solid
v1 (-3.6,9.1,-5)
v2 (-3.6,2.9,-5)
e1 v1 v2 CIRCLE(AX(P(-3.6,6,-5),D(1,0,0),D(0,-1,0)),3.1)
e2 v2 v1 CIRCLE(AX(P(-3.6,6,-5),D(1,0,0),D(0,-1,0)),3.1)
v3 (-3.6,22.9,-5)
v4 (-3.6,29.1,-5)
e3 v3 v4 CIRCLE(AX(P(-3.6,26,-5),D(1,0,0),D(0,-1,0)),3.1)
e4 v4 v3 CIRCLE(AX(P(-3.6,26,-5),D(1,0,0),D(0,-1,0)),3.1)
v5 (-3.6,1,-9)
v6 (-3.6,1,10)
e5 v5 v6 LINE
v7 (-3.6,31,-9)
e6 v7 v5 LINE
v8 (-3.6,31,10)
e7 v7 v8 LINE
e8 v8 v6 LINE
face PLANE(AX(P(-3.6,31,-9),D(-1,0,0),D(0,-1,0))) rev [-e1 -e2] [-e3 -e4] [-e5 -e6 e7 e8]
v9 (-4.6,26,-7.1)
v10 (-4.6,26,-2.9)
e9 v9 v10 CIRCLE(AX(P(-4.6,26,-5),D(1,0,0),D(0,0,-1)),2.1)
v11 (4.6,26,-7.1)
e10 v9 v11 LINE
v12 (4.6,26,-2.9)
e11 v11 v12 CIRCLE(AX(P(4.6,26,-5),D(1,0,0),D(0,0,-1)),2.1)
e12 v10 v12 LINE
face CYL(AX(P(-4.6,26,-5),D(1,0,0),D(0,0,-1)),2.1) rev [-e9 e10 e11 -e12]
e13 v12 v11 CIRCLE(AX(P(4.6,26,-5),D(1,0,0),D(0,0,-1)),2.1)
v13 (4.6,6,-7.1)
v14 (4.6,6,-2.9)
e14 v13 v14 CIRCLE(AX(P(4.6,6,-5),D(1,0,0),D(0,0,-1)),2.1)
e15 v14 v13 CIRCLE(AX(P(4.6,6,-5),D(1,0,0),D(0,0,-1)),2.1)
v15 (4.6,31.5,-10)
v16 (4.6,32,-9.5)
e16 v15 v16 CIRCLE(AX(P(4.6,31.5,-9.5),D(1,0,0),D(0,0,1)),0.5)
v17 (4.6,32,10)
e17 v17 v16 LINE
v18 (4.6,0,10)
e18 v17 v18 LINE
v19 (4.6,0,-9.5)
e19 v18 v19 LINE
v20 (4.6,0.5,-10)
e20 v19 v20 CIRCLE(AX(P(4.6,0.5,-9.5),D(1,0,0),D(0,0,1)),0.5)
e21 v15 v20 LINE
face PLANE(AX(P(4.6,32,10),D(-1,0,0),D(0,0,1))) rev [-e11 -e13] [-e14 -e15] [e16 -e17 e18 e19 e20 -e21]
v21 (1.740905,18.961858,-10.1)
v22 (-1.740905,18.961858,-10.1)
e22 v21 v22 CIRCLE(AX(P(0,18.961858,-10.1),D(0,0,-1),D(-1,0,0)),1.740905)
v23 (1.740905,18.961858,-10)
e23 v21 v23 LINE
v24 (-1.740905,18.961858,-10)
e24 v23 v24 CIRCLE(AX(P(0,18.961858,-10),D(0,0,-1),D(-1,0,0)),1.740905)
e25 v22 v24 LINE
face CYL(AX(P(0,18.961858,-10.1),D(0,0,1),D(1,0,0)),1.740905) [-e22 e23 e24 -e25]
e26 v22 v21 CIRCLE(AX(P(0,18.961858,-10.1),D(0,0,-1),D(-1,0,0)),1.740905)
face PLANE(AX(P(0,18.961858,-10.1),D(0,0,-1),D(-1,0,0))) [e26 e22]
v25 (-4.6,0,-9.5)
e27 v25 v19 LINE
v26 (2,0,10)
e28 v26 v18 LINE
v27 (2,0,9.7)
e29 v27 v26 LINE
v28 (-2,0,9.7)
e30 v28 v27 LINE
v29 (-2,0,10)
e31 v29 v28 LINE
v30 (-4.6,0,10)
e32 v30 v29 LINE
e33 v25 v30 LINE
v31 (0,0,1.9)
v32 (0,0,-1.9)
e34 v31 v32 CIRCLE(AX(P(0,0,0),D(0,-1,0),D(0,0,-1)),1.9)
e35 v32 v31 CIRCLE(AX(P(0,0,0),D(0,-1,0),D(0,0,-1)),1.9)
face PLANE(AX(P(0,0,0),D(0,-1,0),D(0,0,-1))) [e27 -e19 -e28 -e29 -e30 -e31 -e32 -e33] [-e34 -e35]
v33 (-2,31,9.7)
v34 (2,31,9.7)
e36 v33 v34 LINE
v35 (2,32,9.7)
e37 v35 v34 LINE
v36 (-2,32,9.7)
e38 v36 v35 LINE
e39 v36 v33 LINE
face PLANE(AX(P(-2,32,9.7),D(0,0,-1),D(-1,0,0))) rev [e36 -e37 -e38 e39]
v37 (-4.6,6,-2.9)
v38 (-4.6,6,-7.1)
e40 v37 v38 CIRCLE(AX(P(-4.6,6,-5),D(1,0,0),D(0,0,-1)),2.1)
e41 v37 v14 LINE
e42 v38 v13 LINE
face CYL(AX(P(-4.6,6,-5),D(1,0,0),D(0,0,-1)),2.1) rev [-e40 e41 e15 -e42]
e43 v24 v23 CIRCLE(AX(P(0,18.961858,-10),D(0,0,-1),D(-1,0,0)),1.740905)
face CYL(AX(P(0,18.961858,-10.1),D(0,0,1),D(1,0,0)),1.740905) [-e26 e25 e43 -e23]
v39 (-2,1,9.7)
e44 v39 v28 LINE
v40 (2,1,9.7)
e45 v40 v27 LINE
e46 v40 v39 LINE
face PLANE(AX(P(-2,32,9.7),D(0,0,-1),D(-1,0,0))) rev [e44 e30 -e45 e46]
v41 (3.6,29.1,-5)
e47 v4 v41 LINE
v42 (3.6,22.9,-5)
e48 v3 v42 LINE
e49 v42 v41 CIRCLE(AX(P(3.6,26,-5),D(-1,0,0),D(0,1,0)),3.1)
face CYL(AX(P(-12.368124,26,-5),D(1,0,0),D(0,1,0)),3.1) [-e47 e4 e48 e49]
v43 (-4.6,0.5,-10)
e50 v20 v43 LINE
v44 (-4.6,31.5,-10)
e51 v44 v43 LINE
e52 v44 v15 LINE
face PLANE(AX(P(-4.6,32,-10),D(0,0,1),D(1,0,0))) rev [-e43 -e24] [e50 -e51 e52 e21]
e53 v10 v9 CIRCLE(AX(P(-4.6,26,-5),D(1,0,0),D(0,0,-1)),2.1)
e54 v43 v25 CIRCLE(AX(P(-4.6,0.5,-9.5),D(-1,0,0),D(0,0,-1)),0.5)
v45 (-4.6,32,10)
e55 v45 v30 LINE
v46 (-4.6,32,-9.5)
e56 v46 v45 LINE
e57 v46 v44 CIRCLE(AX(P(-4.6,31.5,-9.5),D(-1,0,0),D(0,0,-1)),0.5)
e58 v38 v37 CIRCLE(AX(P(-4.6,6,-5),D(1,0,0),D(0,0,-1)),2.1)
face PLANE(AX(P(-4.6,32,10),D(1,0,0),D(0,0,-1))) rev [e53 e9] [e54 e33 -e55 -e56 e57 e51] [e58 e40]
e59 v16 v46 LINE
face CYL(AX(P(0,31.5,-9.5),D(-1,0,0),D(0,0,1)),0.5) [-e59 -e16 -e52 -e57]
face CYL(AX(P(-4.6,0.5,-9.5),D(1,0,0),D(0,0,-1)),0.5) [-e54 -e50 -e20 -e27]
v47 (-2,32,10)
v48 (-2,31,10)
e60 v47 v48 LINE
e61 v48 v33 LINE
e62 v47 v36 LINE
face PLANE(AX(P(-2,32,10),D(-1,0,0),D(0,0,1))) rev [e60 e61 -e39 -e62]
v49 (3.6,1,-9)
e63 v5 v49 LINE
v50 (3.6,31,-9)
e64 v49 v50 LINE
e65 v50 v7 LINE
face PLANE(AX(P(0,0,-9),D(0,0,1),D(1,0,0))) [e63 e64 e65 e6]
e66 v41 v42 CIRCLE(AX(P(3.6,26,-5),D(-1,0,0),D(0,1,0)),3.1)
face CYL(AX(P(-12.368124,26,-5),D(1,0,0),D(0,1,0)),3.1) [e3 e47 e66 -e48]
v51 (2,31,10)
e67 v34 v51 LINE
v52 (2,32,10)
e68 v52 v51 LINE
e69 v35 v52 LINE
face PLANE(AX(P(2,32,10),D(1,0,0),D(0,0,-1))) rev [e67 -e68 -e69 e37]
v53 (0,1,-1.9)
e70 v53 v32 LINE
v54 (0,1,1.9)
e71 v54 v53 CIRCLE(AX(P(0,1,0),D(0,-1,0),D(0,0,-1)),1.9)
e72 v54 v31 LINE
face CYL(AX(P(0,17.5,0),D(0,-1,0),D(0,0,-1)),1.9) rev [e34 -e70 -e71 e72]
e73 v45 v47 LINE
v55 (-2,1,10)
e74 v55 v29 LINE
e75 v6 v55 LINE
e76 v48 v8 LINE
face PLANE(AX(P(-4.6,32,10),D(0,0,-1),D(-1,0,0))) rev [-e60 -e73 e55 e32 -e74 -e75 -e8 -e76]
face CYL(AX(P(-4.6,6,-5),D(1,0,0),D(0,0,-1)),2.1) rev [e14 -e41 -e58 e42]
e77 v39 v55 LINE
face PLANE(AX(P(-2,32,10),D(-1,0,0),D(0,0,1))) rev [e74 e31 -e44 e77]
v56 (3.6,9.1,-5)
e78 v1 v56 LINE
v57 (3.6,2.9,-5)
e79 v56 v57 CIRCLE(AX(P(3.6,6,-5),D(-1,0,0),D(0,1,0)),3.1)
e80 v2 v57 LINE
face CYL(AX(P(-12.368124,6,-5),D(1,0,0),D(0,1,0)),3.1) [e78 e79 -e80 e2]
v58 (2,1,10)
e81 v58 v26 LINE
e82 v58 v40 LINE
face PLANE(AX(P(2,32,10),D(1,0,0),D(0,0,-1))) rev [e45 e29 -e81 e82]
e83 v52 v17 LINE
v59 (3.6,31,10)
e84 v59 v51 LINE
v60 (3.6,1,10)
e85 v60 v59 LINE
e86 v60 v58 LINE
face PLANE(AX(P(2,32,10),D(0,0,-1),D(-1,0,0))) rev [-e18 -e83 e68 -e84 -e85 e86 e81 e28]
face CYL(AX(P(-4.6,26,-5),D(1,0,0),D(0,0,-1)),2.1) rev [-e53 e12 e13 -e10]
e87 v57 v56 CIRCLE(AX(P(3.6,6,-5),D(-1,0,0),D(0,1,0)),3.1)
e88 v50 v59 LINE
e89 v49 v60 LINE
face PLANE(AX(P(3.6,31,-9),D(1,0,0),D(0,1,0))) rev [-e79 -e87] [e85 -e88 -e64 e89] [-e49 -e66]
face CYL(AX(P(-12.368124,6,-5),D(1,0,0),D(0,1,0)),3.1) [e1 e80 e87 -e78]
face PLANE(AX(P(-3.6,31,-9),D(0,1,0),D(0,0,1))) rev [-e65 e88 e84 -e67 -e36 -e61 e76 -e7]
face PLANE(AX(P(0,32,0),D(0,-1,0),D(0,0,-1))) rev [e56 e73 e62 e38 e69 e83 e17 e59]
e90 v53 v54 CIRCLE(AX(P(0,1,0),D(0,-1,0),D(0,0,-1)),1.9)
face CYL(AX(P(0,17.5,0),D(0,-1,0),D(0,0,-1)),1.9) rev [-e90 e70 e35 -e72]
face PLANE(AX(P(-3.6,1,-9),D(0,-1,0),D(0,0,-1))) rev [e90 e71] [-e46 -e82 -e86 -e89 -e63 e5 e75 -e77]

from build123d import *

# Parameters (mm, degrees)
BOSS_EXTRUDE1_DEPTH = 32
SKETCH2_R           = 2.1
CUT_EXTRUDE1_DEPTH  = 35.76550014
SKETCH3_R           = 1.740904785
BOSS_EXTRUDE2_DEPTH = 0.1
SKETCH4_R           = 3.5
BOSS_EXTRUDE3_DEPTH = 4
SKETCH5_R           = 2.5
BOSS_EXTRUDE4_DEPTH = 62
FILLET1_R           = 0.2
FILLET2_R           = 0.5
SKETCH6_W           = 7.2
SKETCH6_H           = 30
CUT_EXTRUDE2_DEPTH  = 19
SKETCH7_W           = 16.27166032
SKETCH7_H           = 23.629900988
CUT_EXTRUDE3_DEPTH  = 74.5
SKETCH8_R           = 1.9
CUT_EXTRUDE4_DEPTH  = 17.5
SKETCH9_R           = 3.1
SKETCH9_R_2         = 2.1
BOSS_EXTRUDE5_DEPTH = 7.2


with BuildPart() as part:
    # Sketch1 → Boss-Extrude1 (new body)
    with BuildSketch(Plane(origin=(0, 0, 0), x_dir=(1, 0, 0), z_dir=(0, 1, 0))):
        Polygon((2, -10), (4.6, -10), (4.6, 10), (-4.6, 10), (-4.6, -10), (-2, -10), (-2, -9.7), (2, -9.7), align=None)
    extrude(amount=BOSS_EXTRUDE1_DEPTH)

    # Sketch2 → Cut-Extrude1 (cut, through all)
    with BuildSketch(Plane(origin=(4.6, 0, 0), x_dir=(0, 0, -1), z_dir=(1, 0, 0))):
        with Locations((5, 26)):
            Circle(SKETCH2_R)
        with Locations((5, 6)):
            Circle(SKETCH2_R)
    extrude(amount=-CUT_EXTRUDE1_DEPTH, mode=Mode.SUBTRACT)

    # Sketch3 → Boss-Extrude2 (add)
    with BuildSketch(Plane(origin=(0, 0, -10), x_dir=(-1, 0, 0), z_dir=(0, 0, -1))):
        with Locations((0, 18.961857961)):
            Circle(SKETCH3_R)
    extrude(amount=BOSS_EXTRUDE2_DEPTH)

    # Sketch4 → Boss-Extrude3 (add)
    with BuildSketch(Plane.XZ):
        with Locations(Location((0, 0, 0), (0, 0, 270))):
            Circle(SKETCH4_R)
    extrude(amount=BOSS_EXTRUDE3_DEPTH)

    # Sketch5 → Boss-Extrude4 (add)
    with BuildSketch(Plane.XZ.offset(4)):
        with Locations(Location((0, 0, 0), (0, 0, 270))):
            Circle(SKETCH5_R)
    extrude(amount=BOSS_EXTRUDE4_DEPTH)

    # Fillet1
    fillet1_edges = [part.edges().sort_by_distance(p)[0] for p in [
        (0, -4, 3.5),
    ]]
    fillet(fillet1_edges, radius=FILLET1_R)

    # Fillet2
    fillet2_edges = [part.edges().sort_by_distance(p)[0] for p in [
        (0, 0, -10),
        (0, 32, -10),
    ]]
    fillet(fillet2_edges, radius=FILLET2_R)

    # Sketch6 → Cut-Extrude2 (cut)
    with BuildSketch(Plane.XY.offset(10)):
        with Locations((0, 16)):
            Rectangle(SKETCH6_W, SKETCH6_H)
    extrude(amount=-CUT_EXTRUDE2_DEPTH, mode=Mode.SUBTRACT)

    # Sketch7 → Cut-Extrude3 (cut)
    with BuildSketch(Plane.XZ):
        with Locations((-4.097079532, -5.79987022)):
            Rectangle(SKETCH7_W, SKETCH7_H)
    extrude(amount=CUT_EXTRUDE3_DEPTH, mode=Mode.SUBTRACT)

    # Sketch8 → Cut-Extrude4 (cut)
    with BuildSketch(Plane.XZ):
        with Locations(Location((0, 0, 0), (0, 0, 270))):
            Circle(SKETCH8_R)
    extrude(amount=-CUT_EXTRUDE4_DEPTH, mode=Mode.SUBTRACT)

    # Sketch9 → Boss-Extrude5 (add)
    # profile 1 of 2: a face of its own
    with BuildSketch(Plane.ZY.offset(-3.6)):
        with Locations(Location((-5, 26, 0), (0, 0, 90))):
            Circle(SKETCH9_R)
        with Locations(Location((-5, 26, 0), (0, 0, 180))):
            Circle(SKETCH9_R_2, mode=Mode.SUBTRACT)
    # profile 2 of 2: a face of its own
    with BuildSketch(Plane.ZY.offset(-3.6)):
        with Locations(Location((-5, 6, 0), (0, 0, 90))):
            Circle(SKETCH9_R)
        with Locations(Location((-5, 6, 0), (0, 0, 180))):
            Circle(SKETCH9_R_2, mode=Mode.SUBTRACT)
    extrude(amount=BOSS_EXTRUDE5_DEPTH)


solid = part.part
